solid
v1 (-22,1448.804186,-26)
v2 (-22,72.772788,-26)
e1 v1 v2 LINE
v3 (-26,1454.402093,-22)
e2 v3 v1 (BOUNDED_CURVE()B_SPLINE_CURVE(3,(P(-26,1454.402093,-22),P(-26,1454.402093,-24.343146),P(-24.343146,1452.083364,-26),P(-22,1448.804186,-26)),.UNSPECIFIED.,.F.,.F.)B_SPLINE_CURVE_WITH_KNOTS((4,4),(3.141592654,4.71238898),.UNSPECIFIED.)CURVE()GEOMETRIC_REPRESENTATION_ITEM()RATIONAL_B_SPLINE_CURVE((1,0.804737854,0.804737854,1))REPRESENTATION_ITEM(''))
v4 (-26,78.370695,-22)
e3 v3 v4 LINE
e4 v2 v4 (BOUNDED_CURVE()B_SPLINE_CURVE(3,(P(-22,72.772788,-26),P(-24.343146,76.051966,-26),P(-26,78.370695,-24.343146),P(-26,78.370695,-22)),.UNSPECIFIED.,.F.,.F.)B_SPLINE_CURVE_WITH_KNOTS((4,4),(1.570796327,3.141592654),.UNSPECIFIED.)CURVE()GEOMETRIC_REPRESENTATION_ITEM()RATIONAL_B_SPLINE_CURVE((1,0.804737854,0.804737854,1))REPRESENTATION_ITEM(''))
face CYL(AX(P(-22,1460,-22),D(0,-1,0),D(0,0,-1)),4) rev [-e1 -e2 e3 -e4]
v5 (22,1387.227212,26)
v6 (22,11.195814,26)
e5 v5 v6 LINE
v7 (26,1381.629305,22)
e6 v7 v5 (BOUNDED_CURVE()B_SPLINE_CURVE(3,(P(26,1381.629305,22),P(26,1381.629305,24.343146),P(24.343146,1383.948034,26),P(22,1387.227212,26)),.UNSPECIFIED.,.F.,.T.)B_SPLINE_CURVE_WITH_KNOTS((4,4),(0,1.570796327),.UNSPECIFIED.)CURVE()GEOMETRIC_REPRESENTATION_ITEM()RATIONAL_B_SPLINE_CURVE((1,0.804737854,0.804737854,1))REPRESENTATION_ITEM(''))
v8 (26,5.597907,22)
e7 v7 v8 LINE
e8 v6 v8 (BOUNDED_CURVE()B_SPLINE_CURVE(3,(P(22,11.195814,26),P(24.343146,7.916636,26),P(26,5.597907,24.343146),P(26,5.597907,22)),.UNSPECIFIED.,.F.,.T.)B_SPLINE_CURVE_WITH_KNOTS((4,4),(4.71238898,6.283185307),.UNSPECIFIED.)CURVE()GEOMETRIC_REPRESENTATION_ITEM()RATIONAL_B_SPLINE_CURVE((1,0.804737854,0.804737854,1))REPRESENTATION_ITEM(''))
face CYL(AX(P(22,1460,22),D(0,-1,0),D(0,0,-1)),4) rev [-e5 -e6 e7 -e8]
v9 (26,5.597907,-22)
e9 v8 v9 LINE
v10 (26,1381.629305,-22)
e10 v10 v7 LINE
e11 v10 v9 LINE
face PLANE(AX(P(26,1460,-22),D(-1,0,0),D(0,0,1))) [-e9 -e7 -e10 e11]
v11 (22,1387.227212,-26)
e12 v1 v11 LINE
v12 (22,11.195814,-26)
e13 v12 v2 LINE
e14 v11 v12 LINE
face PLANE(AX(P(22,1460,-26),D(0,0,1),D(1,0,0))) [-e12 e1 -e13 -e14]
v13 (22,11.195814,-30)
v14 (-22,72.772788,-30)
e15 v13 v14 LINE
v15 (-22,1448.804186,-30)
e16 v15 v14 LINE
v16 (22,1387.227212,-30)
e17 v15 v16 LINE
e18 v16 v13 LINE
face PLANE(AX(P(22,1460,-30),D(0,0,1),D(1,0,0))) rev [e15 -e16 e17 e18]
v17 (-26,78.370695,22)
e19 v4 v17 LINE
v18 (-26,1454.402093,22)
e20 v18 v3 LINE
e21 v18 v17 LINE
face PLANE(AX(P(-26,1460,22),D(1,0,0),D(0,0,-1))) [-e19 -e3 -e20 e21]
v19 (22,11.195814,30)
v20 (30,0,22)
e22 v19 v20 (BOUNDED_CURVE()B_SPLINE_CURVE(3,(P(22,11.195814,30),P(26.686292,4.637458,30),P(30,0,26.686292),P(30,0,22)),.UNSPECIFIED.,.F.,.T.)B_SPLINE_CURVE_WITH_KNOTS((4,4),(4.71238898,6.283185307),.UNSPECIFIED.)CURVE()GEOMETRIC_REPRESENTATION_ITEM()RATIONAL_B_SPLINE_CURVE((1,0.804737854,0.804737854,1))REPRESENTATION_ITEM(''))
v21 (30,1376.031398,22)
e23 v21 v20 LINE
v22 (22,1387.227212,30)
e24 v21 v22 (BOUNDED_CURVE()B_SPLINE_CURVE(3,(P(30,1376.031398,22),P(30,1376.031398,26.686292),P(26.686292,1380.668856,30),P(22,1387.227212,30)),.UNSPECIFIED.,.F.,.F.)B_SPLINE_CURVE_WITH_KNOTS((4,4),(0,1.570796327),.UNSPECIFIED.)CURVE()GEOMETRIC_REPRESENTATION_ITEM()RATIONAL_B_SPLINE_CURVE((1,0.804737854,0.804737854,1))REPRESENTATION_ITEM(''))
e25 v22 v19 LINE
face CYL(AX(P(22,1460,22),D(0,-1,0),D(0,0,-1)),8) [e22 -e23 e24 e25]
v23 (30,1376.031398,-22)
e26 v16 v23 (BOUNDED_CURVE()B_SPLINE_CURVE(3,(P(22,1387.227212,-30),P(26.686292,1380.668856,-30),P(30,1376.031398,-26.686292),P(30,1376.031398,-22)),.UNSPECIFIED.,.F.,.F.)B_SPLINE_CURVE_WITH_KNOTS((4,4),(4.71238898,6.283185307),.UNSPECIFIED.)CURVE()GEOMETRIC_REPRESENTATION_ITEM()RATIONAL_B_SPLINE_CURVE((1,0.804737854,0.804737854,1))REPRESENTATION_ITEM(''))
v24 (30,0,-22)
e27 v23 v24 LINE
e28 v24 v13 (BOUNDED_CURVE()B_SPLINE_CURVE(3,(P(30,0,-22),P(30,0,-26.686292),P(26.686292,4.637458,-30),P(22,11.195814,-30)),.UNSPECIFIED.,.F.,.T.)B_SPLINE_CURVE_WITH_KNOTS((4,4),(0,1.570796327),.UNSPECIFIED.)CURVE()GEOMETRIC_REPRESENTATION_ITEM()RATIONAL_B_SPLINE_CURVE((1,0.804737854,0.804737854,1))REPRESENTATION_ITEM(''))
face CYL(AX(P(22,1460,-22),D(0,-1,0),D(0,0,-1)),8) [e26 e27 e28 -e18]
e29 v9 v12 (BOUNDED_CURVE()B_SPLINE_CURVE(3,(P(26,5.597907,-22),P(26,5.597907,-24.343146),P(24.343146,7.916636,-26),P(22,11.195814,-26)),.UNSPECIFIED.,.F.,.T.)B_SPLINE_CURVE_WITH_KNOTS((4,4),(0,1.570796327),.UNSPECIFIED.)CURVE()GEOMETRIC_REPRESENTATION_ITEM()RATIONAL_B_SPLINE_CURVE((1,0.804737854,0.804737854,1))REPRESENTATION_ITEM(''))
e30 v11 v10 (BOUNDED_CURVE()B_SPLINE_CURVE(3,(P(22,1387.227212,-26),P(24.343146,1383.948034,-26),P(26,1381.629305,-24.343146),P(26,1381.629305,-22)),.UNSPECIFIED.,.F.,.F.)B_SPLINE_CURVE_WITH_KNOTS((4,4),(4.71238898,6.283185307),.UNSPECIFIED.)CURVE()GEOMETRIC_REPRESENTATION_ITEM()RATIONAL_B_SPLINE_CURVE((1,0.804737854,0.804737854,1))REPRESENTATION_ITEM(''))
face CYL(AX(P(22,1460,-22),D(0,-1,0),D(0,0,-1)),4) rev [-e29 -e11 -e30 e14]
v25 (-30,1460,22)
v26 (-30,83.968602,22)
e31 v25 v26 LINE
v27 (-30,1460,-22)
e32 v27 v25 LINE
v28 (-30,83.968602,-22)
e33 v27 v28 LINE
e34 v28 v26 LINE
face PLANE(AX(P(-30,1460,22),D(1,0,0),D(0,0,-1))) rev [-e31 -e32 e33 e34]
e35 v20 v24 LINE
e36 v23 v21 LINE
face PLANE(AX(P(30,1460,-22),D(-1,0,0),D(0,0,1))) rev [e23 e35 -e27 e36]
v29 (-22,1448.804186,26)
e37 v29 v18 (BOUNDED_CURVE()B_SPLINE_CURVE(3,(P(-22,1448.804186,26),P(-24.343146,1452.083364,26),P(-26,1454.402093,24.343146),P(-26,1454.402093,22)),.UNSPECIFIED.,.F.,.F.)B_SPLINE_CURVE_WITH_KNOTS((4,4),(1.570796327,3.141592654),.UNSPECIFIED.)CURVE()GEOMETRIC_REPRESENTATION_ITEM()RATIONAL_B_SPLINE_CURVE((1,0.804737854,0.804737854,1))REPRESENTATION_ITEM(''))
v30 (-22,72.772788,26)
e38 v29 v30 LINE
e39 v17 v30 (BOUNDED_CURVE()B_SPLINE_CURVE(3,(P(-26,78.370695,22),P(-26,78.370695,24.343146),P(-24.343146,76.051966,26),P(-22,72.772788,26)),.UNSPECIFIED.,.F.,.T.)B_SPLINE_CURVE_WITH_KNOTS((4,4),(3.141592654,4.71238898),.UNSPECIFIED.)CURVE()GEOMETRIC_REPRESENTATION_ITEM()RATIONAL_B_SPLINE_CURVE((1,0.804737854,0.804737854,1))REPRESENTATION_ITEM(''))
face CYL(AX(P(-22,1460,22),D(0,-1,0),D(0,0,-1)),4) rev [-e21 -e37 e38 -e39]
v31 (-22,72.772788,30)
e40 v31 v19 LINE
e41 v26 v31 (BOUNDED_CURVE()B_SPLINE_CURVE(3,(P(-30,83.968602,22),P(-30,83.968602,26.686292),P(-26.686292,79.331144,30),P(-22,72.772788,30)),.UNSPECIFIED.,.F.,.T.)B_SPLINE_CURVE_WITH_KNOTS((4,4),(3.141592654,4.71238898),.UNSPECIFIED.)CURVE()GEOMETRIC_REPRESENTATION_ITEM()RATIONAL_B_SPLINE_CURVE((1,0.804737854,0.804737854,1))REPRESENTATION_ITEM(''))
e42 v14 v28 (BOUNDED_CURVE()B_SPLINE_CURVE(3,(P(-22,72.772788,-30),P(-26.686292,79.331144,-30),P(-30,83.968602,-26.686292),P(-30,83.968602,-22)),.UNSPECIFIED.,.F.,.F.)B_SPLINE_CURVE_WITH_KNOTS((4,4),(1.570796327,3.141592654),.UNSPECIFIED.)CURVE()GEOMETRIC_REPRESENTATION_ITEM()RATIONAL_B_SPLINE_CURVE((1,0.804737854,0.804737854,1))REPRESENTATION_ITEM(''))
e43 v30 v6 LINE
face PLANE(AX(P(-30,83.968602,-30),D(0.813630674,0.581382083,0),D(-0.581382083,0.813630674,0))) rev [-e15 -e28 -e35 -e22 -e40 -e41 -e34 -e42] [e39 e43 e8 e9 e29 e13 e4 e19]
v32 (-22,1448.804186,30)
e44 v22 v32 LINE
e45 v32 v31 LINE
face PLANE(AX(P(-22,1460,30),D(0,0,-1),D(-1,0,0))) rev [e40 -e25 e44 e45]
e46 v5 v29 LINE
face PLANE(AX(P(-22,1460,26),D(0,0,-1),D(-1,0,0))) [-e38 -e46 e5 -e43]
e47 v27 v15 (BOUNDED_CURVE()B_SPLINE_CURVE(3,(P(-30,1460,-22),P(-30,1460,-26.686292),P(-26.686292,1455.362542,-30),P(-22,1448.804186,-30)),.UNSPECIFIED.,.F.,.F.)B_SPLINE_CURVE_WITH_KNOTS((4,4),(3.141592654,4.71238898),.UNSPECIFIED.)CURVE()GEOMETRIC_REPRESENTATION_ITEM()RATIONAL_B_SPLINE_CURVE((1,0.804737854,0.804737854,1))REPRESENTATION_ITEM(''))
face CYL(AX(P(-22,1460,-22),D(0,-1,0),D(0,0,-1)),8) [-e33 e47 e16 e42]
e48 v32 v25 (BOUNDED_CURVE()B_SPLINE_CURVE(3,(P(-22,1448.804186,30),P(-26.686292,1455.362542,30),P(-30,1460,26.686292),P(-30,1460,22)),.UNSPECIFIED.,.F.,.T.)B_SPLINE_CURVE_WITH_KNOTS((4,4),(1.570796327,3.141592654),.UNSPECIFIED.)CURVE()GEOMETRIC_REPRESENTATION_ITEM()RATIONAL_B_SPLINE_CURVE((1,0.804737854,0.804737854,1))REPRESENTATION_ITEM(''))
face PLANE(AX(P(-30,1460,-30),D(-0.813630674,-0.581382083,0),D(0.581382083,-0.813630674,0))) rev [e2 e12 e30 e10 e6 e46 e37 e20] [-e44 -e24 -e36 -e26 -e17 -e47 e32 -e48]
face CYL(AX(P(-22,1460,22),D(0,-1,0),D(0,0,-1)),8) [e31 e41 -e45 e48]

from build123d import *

# Parameters (mm, degrees)
GB_T_6728_2002_SQUARE_HOLLOW_SECTION_60_DEPTH = 1460
CUT_EXTRUDE1_DEPTH                            = 1462.5402834
CUT_EXTRUDE1_DEPTH_BACK                       = 1462.5402834


with BuildPart() as part:
    # Sketch1 → GB/T 6728-2002 square hollow section 60×60×4(1) (new body)
    with BuildSketch(Plane(origin=(0, 0, 0), x_dir=(-1, 0, 0), z_dir=(0, 1, 0))):
        with BuildLine():
            Line((-22, -30), (22, -30))
            ThreePointArc((22, -30), (27.656854249, -27.656854249), (30, -22))
            Line((30, -22), (30, 22))
            ThreePointArc((30, 22), (27.656854249, 27.656854249), (22, 30))
            Line((22, 30), (-22, 30))
            ThreePointArc((-22, 30), (-27.656854249, 27.656854249), (-30, 22))
            Line((-30, 22), (-30, -22))
            ThreePointArc((-30, -22), (-27.656854249, -27.656854249), (-22, -30))
        make_face()
        with BuildLine():
            Line((-22, -26), (22, -26))
            ThreePointArc((22, -26), (24.828427125, -24.828427125), (26, -22))
            Line((26, -22), (26, 22))
            ThreePointArc((26, 22), (24.828427125, 24.828427125), (22, 26))
            Line((22, 26), (-22, 26))
            ThreePointArc((-22, 26), (-24.828427125, 24.828427125), (-26, 22))
            Line((-26, 22), (-26, -22))
            ThreePointArc((-26, -22), (-24.828427125, -24.828427125), (-22, -26))
        make_face(mode=Mode.SUBTRACT)
    extrude(amount=GB_T_6728_2002_SQUARE_HOLLOW_SECTION_60_DEPTH)

    # Sketch2 → Cut-Extrude1 (cut, two sides: drawn at the far end of the back side and taken through both)
    with BuildSketch(Plane.XY.offset(30).offset(-CUT_EXTRUDE1_DEPTH_BACK)):
        Polygon((-30, 1460), (30, 1376.03139841), (30, 1460), align=None)
        Polygon((-30, 0), (-30, 83.96860159), (30, 0), align=None)
    extrude(amount=CUT_EXTRUDE1_DEPTH + CUT_EXTRUDE1_DEPTH_BACK, mode=Mode.SUBTRACT)


solid = part.part
